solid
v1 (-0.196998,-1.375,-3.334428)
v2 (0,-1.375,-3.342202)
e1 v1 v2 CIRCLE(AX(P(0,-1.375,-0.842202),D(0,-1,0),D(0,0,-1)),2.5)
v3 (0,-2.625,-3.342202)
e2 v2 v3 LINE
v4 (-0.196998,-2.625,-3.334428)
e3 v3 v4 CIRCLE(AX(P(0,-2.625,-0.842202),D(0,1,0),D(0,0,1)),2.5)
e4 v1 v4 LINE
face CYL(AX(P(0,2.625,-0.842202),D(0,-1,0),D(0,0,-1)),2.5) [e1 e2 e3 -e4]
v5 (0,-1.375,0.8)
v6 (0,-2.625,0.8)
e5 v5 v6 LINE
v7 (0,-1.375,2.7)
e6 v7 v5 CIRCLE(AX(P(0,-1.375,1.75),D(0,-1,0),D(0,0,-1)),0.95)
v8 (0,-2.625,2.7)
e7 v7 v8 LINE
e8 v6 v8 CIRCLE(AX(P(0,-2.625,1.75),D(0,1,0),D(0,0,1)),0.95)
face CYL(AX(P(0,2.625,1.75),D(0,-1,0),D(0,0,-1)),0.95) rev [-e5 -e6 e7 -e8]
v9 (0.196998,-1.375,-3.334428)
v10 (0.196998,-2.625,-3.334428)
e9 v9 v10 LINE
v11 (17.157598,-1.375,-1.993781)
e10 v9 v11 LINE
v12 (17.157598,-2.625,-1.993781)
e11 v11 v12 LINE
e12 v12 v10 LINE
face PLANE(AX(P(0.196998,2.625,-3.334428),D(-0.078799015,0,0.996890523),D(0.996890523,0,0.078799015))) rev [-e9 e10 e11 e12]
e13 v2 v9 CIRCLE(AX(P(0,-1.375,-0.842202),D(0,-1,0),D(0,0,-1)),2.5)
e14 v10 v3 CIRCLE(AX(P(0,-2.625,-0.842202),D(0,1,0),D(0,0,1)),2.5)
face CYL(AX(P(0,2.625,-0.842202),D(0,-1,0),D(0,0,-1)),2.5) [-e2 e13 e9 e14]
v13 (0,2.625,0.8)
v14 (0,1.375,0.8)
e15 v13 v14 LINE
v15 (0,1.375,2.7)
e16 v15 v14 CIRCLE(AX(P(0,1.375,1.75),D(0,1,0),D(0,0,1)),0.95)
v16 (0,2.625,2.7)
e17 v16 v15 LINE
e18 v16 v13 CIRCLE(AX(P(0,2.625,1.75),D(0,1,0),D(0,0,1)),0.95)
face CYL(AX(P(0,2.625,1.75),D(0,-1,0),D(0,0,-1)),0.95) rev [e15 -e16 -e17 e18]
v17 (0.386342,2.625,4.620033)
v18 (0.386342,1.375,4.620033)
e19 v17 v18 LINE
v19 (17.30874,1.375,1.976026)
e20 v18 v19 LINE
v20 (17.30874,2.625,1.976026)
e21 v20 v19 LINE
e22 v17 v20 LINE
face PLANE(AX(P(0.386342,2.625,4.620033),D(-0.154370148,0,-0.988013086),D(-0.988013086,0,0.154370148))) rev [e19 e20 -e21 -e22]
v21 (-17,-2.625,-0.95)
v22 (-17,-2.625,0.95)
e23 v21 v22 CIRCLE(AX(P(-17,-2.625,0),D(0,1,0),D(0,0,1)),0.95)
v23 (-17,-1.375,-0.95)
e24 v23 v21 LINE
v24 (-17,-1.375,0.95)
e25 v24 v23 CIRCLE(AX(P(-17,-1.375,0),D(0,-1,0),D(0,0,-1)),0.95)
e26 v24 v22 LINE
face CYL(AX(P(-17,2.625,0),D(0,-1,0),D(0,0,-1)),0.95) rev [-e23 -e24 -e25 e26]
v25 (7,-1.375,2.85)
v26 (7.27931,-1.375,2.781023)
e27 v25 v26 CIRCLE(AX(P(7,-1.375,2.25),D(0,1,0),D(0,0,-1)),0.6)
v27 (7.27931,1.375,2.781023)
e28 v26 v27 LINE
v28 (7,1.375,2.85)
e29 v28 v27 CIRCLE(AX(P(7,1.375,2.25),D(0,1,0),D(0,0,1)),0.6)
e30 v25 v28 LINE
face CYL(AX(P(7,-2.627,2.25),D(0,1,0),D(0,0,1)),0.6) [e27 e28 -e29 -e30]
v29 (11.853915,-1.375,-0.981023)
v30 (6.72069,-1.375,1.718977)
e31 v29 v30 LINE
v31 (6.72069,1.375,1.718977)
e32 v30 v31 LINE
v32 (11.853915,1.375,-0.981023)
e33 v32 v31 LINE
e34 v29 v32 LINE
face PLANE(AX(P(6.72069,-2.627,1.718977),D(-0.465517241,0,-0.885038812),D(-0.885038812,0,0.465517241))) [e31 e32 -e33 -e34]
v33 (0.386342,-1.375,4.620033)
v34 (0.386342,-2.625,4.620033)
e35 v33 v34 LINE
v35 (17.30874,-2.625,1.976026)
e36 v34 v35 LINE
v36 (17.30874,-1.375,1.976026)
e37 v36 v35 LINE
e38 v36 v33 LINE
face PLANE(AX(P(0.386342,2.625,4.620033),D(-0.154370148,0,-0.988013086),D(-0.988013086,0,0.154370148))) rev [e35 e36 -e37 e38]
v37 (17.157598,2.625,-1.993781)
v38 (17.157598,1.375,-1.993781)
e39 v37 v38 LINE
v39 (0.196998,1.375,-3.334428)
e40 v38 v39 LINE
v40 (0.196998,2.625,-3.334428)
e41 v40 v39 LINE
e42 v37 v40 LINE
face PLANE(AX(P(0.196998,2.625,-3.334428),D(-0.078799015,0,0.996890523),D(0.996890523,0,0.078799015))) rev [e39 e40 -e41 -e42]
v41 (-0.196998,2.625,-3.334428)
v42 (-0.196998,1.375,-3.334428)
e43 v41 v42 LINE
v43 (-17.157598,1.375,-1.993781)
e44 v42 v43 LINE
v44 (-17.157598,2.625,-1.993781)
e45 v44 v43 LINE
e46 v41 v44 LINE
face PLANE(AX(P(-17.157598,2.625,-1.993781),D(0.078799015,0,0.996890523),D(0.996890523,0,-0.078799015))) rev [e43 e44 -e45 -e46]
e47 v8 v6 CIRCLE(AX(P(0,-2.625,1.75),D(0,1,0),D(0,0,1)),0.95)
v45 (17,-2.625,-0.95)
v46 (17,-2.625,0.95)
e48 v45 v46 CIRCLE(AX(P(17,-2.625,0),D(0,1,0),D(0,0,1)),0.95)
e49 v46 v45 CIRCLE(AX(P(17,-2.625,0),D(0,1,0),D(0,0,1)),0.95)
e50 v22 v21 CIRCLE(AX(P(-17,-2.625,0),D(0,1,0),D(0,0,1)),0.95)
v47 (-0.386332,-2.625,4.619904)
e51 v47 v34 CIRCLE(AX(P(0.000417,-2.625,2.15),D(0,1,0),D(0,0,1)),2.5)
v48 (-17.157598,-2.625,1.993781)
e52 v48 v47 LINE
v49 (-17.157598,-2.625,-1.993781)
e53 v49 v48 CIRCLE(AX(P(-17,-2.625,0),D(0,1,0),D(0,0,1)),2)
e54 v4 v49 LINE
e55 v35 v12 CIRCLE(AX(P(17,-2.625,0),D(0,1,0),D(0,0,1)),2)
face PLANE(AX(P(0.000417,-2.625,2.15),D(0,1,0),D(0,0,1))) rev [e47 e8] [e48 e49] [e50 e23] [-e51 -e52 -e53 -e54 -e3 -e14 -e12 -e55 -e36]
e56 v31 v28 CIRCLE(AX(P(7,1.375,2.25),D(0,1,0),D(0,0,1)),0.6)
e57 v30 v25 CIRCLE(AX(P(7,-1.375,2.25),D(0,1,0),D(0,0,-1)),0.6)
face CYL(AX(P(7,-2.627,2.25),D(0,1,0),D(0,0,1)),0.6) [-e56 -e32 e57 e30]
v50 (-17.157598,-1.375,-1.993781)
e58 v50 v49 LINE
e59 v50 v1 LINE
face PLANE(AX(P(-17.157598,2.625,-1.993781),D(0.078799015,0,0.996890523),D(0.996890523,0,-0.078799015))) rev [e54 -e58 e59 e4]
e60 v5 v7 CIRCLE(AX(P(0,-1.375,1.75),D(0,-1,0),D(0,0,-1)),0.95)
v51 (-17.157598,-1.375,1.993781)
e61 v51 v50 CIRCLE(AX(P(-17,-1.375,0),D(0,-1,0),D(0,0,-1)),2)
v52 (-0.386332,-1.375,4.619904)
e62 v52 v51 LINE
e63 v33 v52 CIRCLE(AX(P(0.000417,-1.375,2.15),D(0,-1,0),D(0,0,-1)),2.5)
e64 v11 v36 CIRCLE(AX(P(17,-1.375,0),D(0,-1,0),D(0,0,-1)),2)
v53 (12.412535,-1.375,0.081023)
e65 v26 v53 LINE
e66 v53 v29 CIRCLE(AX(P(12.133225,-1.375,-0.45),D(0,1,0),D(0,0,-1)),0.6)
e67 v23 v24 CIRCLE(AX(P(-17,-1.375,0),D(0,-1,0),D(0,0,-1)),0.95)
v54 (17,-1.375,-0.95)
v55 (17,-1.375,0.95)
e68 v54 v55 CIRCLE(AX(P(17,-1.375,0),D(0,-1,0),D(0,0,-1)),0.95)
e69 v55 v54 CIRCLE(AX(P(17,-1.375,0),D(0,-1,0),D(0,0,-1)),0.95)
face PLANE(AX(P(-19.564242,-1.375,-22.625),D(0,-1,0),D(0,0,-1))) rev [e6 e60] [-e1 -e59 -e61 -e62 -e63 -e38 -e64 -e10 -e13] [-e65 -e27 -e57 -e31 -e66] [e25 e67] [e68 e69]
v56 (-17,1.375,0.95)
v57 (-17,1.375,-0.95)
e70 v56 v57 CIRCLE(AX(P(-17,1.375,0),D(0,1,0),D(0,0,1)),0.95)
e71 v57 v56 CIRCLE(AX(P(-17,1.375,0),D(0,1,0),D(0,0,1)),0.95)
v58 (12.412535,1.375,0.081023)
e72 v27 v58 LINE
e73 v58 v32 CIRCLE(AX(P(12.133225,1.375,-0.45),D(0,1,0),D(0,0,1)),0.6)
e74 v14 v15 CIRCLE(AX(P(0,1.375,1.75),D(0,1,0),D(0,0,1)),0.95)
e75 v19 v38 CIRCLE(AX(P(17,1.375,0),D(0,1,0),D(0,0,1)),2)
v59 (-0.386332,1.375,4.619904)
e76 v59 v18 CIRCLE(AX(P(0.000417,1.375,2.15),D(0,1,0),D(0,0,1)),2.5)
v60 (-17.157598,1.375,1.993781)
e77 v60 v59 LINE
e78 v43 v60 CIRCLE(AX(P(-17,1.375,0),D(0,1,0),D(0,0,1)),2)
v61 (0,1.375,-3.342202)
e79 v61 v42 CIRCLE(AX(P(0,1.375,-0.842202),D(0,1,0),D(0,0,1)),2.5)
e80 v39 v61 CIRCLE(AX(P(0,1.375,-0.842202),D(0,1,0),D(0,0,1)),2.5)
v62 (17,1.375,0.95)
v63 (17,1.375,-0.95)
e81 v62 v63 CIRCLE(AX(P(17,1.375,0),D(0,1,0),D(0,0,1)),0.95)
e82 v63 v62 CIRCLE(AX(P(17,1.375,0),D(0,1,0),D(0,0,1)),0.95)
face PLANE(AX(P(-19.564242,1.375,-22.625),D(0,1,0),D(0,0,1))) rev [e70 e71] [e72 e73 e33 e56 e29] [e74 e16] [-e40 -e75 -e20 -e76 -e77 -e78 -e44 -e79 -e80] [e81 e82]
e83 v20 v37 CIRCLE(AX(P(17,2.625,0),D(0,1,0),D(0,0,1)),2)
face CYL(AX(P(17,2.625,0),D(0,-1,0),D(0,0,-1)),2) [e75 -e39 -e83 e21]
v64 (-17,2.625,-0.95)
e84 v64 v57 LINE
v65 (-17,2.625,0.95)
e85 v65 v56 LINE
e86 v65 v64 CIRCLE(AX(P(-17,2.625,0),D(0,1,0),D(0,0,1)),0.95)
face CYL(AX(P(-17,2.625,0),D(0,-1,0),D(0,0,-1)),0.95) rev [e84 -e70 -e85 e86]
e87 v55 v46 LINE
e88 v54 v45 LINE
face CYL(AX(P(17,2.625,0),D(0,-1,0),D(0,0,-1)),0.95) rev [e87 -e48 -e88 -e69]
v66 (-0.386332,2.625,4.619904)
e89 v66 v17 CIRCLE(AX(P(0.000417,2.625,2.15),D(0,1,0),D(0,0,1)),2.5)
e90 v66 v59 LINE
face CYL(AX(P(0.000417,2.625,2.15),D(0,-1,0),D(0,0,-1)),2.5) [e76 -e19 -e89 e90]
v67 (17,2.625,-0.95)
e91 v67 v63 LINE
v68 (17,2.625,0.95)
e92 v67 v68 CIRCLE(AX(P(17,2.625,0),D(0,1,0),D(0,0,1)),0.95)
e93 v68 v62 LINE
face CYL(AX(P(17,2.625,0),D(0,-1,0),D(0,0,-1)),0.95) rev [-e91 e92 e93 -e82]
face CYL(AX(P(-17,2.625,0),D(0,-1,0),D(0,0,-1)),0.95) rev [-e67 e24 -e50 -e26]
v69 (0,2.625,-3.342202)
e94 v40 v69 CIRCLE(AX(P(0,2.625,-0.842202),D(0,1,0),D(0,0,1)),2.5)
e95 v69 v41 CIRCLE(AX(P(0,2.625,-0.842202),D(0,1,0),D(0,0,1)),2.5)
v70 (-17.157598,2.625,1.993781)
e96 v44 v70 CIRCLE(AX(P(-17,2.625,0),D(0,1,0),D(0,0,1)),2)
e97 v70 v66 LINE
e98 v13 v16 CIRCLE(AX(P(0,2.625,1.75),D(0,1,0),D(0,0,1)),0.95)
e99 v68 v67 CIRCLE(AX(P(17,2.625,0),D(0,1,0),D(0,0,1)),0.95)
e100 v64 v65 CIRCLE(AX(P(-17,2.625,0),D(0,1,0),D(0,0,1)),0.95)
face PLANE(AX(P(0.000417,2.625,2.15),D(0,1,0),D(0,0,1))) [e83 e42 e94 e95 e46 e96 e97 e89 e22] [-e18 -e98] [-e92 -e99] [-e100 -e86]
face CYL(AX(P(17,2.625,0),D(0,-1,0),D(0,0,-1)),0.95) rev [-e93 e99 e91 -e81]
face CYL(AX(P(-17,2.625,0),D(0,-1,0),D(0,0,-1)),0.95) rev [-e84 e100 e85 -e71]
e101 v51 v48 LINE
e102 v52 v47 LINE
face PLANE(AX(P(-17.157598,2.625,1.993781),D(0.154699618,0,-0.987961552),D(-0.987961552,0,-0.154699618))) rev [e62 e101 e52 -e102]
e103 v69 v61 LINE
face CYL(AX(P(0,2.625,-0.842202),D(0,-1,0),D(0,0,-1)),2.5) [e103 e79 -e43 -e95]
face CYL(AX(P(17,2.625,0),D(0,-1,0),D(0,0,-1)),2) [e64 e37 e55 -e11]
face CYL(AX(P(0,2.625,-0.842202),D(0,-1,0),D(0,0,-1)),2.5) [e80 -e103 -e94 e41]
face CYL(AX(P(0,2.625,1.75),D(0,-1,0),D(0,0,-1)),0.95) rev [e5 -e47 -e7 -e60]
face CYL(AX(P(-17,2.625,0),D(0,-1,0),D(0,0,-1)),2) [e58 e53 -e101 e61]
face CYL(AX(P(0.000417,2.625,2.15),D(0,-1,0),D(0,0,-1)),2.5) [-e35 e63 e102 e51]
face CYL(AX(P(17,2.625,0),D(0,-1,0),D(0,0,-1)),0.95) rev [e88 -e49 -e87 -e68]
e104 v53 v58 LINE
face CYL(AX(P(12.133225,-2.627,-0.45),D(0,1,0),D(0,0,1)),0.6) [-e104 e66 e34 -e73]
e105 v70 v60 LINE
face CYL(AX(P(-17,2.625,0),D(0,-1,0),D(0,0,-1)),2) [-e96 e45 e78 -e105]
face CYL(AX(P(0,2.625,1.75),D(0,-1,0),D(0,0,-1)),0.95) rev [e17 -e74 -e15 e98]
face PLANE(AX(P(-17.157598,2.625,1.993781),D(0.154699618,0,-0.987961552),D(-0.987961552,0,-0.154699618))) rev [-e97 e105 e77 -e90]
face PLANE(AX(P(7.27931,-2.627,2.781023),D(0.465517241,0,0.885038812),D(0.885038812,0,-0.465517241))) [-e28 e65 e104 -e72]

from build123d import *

# Parameters (mm, degrees)
ARM_PROFILE_SKETCH_R  = 0.95
ARM_BODY_DEPTH        = 2.625
FORK_SLOT_SKETCH_W    = 39.128483504
FORK_SLOT_SKETCH_H    = 2.75
FORK_SLOT_CUT_DEPTH   = 22.625
CENTRE_WEB_DEPTH      = 2.625
CENTRE_WEB_DEPTH_BACK = 1.375


with BuildPart() as part:
    # Arm Profile Sketch → Arm Body (new, symmetric)
    with BuildSketch(Plane(origin=(0, 0, 0), x_dir=(1, 0, 0), z_dir=(0, 1, 0))):
        with BuildLine():
            Line((-17.15759803, 1.993781046), (-0.196997537, 3.334428369))
            ThreePointArc((-0.196997537, 3.334428369), (0, 3.342202061), (0.196997537, 3.334428369))
            Line((0.196997537, 3.334428369), (17.15759803, 1.993781046))
            ThreePointArc((17.15759803, 1.993781046), (18.998552025, 0.076090769), (17.308740296, -1.976026171))
            Line((17.308740296, -1.976026171), (0.386342216, -4.620032749))
            ThreePointArc((0.386342216, -4.620032749), (0, -4.65), (-0.386332201, -4.619903915))
            Line((-0.386332201, -4.619903915), (-17.15759803, -1.993781046))
            ThreePointArc((-17.15759803, -1.993781046), (-19, 0), (-17.15759803, 1.993781046))
        make_face()
        with Locations(Location((-17, 0, 0), (0, 0, 90))):
            Circle(ARM_PROFILE_SKETCH_R, mode=Mode.SUBTRACT)
        with Locations(Location((17, 0, 0), (0, 0, 90))):
            Circle(ARM_PROFILE_SKETCH_R, mode=Mode.SUBTRACT)
        with Locations(Location((0, -1.75, 0), (0, 0, 90))):
            Circle(ARM_PROFILE_SKETCH_R, mode=Mode.SUBTRACT)
    extrude(amount=ARM_BODY_DEPTH, both=True)

    # Fork Slot Sketch → Fork Slot Cut (cut, symmetric)
    with BuildSketch(Plane.XY):
        Rectangle(FORK_SLOT_SKETCH_W, FORK_SLOT_SKETCH_H)
    extrude(amount=FORK_SLOT_CUT_DEPTH, both=True, mode=Mode.SUBTRACT)


with BuildPart() as fork_slot_cut_piece_1:
    # of the separate pieces the step leaves, piece 1, a body of its own (fork_slot_cut_pieces)
    add(part.part.solids().sort_by_distance((-0.386332201, -2.625, 4.619903915))[0])



with BuildPart() as fork_slot_cut_piece_2:
    # of the separate pieces the step leaves, piece 2, a body of its own (fork_slot_cut_pieces)
    add(part.part.solids().sort_by_distance((-0.386332201, 1.375, 4.619903915))[0])


with BuildPart() as fork_slot_cut_piece_1_1:
    add(fork_slot_cut_piece_1.part)

    add(fork_slot_cut_piece_2.part)  # Centre Web merges Fork Slot Cut piece 2
    # Centre Web Sketch → Centre Web (add, two sides: drawn at the far end of the back side and taken through both)
    with BuildSketch(Plane(origin=(0, 0, 0), x_dir=(1, 0, 0), z_dir=(0, 1, 0)).offset(-CENTRE_WEB_DEPTH_BACK)):
        with BuildLine():
            Line((6.720689655, -1.718976713), (11.853914762, 0.981023287))
            ThreePointArc((11.853914762, 0.981023287), (12.664248394, 0.729310345), (12.412535452, -0.081023287))
            Line((12.412535452, -0.081023287), (7.279310345, -2.781023287))
            ThreePointArc((7.279310345, -2.781023287), (6.468976713, -2.529310345), (6.720689655, -1.718976713))
        make_face()
    extrude(amount=CENTRE_WEB_DEPTH + CENTRE_WEB_DEPTH_BACK)


solid = fork_slot_cut_piece_1_1.part
